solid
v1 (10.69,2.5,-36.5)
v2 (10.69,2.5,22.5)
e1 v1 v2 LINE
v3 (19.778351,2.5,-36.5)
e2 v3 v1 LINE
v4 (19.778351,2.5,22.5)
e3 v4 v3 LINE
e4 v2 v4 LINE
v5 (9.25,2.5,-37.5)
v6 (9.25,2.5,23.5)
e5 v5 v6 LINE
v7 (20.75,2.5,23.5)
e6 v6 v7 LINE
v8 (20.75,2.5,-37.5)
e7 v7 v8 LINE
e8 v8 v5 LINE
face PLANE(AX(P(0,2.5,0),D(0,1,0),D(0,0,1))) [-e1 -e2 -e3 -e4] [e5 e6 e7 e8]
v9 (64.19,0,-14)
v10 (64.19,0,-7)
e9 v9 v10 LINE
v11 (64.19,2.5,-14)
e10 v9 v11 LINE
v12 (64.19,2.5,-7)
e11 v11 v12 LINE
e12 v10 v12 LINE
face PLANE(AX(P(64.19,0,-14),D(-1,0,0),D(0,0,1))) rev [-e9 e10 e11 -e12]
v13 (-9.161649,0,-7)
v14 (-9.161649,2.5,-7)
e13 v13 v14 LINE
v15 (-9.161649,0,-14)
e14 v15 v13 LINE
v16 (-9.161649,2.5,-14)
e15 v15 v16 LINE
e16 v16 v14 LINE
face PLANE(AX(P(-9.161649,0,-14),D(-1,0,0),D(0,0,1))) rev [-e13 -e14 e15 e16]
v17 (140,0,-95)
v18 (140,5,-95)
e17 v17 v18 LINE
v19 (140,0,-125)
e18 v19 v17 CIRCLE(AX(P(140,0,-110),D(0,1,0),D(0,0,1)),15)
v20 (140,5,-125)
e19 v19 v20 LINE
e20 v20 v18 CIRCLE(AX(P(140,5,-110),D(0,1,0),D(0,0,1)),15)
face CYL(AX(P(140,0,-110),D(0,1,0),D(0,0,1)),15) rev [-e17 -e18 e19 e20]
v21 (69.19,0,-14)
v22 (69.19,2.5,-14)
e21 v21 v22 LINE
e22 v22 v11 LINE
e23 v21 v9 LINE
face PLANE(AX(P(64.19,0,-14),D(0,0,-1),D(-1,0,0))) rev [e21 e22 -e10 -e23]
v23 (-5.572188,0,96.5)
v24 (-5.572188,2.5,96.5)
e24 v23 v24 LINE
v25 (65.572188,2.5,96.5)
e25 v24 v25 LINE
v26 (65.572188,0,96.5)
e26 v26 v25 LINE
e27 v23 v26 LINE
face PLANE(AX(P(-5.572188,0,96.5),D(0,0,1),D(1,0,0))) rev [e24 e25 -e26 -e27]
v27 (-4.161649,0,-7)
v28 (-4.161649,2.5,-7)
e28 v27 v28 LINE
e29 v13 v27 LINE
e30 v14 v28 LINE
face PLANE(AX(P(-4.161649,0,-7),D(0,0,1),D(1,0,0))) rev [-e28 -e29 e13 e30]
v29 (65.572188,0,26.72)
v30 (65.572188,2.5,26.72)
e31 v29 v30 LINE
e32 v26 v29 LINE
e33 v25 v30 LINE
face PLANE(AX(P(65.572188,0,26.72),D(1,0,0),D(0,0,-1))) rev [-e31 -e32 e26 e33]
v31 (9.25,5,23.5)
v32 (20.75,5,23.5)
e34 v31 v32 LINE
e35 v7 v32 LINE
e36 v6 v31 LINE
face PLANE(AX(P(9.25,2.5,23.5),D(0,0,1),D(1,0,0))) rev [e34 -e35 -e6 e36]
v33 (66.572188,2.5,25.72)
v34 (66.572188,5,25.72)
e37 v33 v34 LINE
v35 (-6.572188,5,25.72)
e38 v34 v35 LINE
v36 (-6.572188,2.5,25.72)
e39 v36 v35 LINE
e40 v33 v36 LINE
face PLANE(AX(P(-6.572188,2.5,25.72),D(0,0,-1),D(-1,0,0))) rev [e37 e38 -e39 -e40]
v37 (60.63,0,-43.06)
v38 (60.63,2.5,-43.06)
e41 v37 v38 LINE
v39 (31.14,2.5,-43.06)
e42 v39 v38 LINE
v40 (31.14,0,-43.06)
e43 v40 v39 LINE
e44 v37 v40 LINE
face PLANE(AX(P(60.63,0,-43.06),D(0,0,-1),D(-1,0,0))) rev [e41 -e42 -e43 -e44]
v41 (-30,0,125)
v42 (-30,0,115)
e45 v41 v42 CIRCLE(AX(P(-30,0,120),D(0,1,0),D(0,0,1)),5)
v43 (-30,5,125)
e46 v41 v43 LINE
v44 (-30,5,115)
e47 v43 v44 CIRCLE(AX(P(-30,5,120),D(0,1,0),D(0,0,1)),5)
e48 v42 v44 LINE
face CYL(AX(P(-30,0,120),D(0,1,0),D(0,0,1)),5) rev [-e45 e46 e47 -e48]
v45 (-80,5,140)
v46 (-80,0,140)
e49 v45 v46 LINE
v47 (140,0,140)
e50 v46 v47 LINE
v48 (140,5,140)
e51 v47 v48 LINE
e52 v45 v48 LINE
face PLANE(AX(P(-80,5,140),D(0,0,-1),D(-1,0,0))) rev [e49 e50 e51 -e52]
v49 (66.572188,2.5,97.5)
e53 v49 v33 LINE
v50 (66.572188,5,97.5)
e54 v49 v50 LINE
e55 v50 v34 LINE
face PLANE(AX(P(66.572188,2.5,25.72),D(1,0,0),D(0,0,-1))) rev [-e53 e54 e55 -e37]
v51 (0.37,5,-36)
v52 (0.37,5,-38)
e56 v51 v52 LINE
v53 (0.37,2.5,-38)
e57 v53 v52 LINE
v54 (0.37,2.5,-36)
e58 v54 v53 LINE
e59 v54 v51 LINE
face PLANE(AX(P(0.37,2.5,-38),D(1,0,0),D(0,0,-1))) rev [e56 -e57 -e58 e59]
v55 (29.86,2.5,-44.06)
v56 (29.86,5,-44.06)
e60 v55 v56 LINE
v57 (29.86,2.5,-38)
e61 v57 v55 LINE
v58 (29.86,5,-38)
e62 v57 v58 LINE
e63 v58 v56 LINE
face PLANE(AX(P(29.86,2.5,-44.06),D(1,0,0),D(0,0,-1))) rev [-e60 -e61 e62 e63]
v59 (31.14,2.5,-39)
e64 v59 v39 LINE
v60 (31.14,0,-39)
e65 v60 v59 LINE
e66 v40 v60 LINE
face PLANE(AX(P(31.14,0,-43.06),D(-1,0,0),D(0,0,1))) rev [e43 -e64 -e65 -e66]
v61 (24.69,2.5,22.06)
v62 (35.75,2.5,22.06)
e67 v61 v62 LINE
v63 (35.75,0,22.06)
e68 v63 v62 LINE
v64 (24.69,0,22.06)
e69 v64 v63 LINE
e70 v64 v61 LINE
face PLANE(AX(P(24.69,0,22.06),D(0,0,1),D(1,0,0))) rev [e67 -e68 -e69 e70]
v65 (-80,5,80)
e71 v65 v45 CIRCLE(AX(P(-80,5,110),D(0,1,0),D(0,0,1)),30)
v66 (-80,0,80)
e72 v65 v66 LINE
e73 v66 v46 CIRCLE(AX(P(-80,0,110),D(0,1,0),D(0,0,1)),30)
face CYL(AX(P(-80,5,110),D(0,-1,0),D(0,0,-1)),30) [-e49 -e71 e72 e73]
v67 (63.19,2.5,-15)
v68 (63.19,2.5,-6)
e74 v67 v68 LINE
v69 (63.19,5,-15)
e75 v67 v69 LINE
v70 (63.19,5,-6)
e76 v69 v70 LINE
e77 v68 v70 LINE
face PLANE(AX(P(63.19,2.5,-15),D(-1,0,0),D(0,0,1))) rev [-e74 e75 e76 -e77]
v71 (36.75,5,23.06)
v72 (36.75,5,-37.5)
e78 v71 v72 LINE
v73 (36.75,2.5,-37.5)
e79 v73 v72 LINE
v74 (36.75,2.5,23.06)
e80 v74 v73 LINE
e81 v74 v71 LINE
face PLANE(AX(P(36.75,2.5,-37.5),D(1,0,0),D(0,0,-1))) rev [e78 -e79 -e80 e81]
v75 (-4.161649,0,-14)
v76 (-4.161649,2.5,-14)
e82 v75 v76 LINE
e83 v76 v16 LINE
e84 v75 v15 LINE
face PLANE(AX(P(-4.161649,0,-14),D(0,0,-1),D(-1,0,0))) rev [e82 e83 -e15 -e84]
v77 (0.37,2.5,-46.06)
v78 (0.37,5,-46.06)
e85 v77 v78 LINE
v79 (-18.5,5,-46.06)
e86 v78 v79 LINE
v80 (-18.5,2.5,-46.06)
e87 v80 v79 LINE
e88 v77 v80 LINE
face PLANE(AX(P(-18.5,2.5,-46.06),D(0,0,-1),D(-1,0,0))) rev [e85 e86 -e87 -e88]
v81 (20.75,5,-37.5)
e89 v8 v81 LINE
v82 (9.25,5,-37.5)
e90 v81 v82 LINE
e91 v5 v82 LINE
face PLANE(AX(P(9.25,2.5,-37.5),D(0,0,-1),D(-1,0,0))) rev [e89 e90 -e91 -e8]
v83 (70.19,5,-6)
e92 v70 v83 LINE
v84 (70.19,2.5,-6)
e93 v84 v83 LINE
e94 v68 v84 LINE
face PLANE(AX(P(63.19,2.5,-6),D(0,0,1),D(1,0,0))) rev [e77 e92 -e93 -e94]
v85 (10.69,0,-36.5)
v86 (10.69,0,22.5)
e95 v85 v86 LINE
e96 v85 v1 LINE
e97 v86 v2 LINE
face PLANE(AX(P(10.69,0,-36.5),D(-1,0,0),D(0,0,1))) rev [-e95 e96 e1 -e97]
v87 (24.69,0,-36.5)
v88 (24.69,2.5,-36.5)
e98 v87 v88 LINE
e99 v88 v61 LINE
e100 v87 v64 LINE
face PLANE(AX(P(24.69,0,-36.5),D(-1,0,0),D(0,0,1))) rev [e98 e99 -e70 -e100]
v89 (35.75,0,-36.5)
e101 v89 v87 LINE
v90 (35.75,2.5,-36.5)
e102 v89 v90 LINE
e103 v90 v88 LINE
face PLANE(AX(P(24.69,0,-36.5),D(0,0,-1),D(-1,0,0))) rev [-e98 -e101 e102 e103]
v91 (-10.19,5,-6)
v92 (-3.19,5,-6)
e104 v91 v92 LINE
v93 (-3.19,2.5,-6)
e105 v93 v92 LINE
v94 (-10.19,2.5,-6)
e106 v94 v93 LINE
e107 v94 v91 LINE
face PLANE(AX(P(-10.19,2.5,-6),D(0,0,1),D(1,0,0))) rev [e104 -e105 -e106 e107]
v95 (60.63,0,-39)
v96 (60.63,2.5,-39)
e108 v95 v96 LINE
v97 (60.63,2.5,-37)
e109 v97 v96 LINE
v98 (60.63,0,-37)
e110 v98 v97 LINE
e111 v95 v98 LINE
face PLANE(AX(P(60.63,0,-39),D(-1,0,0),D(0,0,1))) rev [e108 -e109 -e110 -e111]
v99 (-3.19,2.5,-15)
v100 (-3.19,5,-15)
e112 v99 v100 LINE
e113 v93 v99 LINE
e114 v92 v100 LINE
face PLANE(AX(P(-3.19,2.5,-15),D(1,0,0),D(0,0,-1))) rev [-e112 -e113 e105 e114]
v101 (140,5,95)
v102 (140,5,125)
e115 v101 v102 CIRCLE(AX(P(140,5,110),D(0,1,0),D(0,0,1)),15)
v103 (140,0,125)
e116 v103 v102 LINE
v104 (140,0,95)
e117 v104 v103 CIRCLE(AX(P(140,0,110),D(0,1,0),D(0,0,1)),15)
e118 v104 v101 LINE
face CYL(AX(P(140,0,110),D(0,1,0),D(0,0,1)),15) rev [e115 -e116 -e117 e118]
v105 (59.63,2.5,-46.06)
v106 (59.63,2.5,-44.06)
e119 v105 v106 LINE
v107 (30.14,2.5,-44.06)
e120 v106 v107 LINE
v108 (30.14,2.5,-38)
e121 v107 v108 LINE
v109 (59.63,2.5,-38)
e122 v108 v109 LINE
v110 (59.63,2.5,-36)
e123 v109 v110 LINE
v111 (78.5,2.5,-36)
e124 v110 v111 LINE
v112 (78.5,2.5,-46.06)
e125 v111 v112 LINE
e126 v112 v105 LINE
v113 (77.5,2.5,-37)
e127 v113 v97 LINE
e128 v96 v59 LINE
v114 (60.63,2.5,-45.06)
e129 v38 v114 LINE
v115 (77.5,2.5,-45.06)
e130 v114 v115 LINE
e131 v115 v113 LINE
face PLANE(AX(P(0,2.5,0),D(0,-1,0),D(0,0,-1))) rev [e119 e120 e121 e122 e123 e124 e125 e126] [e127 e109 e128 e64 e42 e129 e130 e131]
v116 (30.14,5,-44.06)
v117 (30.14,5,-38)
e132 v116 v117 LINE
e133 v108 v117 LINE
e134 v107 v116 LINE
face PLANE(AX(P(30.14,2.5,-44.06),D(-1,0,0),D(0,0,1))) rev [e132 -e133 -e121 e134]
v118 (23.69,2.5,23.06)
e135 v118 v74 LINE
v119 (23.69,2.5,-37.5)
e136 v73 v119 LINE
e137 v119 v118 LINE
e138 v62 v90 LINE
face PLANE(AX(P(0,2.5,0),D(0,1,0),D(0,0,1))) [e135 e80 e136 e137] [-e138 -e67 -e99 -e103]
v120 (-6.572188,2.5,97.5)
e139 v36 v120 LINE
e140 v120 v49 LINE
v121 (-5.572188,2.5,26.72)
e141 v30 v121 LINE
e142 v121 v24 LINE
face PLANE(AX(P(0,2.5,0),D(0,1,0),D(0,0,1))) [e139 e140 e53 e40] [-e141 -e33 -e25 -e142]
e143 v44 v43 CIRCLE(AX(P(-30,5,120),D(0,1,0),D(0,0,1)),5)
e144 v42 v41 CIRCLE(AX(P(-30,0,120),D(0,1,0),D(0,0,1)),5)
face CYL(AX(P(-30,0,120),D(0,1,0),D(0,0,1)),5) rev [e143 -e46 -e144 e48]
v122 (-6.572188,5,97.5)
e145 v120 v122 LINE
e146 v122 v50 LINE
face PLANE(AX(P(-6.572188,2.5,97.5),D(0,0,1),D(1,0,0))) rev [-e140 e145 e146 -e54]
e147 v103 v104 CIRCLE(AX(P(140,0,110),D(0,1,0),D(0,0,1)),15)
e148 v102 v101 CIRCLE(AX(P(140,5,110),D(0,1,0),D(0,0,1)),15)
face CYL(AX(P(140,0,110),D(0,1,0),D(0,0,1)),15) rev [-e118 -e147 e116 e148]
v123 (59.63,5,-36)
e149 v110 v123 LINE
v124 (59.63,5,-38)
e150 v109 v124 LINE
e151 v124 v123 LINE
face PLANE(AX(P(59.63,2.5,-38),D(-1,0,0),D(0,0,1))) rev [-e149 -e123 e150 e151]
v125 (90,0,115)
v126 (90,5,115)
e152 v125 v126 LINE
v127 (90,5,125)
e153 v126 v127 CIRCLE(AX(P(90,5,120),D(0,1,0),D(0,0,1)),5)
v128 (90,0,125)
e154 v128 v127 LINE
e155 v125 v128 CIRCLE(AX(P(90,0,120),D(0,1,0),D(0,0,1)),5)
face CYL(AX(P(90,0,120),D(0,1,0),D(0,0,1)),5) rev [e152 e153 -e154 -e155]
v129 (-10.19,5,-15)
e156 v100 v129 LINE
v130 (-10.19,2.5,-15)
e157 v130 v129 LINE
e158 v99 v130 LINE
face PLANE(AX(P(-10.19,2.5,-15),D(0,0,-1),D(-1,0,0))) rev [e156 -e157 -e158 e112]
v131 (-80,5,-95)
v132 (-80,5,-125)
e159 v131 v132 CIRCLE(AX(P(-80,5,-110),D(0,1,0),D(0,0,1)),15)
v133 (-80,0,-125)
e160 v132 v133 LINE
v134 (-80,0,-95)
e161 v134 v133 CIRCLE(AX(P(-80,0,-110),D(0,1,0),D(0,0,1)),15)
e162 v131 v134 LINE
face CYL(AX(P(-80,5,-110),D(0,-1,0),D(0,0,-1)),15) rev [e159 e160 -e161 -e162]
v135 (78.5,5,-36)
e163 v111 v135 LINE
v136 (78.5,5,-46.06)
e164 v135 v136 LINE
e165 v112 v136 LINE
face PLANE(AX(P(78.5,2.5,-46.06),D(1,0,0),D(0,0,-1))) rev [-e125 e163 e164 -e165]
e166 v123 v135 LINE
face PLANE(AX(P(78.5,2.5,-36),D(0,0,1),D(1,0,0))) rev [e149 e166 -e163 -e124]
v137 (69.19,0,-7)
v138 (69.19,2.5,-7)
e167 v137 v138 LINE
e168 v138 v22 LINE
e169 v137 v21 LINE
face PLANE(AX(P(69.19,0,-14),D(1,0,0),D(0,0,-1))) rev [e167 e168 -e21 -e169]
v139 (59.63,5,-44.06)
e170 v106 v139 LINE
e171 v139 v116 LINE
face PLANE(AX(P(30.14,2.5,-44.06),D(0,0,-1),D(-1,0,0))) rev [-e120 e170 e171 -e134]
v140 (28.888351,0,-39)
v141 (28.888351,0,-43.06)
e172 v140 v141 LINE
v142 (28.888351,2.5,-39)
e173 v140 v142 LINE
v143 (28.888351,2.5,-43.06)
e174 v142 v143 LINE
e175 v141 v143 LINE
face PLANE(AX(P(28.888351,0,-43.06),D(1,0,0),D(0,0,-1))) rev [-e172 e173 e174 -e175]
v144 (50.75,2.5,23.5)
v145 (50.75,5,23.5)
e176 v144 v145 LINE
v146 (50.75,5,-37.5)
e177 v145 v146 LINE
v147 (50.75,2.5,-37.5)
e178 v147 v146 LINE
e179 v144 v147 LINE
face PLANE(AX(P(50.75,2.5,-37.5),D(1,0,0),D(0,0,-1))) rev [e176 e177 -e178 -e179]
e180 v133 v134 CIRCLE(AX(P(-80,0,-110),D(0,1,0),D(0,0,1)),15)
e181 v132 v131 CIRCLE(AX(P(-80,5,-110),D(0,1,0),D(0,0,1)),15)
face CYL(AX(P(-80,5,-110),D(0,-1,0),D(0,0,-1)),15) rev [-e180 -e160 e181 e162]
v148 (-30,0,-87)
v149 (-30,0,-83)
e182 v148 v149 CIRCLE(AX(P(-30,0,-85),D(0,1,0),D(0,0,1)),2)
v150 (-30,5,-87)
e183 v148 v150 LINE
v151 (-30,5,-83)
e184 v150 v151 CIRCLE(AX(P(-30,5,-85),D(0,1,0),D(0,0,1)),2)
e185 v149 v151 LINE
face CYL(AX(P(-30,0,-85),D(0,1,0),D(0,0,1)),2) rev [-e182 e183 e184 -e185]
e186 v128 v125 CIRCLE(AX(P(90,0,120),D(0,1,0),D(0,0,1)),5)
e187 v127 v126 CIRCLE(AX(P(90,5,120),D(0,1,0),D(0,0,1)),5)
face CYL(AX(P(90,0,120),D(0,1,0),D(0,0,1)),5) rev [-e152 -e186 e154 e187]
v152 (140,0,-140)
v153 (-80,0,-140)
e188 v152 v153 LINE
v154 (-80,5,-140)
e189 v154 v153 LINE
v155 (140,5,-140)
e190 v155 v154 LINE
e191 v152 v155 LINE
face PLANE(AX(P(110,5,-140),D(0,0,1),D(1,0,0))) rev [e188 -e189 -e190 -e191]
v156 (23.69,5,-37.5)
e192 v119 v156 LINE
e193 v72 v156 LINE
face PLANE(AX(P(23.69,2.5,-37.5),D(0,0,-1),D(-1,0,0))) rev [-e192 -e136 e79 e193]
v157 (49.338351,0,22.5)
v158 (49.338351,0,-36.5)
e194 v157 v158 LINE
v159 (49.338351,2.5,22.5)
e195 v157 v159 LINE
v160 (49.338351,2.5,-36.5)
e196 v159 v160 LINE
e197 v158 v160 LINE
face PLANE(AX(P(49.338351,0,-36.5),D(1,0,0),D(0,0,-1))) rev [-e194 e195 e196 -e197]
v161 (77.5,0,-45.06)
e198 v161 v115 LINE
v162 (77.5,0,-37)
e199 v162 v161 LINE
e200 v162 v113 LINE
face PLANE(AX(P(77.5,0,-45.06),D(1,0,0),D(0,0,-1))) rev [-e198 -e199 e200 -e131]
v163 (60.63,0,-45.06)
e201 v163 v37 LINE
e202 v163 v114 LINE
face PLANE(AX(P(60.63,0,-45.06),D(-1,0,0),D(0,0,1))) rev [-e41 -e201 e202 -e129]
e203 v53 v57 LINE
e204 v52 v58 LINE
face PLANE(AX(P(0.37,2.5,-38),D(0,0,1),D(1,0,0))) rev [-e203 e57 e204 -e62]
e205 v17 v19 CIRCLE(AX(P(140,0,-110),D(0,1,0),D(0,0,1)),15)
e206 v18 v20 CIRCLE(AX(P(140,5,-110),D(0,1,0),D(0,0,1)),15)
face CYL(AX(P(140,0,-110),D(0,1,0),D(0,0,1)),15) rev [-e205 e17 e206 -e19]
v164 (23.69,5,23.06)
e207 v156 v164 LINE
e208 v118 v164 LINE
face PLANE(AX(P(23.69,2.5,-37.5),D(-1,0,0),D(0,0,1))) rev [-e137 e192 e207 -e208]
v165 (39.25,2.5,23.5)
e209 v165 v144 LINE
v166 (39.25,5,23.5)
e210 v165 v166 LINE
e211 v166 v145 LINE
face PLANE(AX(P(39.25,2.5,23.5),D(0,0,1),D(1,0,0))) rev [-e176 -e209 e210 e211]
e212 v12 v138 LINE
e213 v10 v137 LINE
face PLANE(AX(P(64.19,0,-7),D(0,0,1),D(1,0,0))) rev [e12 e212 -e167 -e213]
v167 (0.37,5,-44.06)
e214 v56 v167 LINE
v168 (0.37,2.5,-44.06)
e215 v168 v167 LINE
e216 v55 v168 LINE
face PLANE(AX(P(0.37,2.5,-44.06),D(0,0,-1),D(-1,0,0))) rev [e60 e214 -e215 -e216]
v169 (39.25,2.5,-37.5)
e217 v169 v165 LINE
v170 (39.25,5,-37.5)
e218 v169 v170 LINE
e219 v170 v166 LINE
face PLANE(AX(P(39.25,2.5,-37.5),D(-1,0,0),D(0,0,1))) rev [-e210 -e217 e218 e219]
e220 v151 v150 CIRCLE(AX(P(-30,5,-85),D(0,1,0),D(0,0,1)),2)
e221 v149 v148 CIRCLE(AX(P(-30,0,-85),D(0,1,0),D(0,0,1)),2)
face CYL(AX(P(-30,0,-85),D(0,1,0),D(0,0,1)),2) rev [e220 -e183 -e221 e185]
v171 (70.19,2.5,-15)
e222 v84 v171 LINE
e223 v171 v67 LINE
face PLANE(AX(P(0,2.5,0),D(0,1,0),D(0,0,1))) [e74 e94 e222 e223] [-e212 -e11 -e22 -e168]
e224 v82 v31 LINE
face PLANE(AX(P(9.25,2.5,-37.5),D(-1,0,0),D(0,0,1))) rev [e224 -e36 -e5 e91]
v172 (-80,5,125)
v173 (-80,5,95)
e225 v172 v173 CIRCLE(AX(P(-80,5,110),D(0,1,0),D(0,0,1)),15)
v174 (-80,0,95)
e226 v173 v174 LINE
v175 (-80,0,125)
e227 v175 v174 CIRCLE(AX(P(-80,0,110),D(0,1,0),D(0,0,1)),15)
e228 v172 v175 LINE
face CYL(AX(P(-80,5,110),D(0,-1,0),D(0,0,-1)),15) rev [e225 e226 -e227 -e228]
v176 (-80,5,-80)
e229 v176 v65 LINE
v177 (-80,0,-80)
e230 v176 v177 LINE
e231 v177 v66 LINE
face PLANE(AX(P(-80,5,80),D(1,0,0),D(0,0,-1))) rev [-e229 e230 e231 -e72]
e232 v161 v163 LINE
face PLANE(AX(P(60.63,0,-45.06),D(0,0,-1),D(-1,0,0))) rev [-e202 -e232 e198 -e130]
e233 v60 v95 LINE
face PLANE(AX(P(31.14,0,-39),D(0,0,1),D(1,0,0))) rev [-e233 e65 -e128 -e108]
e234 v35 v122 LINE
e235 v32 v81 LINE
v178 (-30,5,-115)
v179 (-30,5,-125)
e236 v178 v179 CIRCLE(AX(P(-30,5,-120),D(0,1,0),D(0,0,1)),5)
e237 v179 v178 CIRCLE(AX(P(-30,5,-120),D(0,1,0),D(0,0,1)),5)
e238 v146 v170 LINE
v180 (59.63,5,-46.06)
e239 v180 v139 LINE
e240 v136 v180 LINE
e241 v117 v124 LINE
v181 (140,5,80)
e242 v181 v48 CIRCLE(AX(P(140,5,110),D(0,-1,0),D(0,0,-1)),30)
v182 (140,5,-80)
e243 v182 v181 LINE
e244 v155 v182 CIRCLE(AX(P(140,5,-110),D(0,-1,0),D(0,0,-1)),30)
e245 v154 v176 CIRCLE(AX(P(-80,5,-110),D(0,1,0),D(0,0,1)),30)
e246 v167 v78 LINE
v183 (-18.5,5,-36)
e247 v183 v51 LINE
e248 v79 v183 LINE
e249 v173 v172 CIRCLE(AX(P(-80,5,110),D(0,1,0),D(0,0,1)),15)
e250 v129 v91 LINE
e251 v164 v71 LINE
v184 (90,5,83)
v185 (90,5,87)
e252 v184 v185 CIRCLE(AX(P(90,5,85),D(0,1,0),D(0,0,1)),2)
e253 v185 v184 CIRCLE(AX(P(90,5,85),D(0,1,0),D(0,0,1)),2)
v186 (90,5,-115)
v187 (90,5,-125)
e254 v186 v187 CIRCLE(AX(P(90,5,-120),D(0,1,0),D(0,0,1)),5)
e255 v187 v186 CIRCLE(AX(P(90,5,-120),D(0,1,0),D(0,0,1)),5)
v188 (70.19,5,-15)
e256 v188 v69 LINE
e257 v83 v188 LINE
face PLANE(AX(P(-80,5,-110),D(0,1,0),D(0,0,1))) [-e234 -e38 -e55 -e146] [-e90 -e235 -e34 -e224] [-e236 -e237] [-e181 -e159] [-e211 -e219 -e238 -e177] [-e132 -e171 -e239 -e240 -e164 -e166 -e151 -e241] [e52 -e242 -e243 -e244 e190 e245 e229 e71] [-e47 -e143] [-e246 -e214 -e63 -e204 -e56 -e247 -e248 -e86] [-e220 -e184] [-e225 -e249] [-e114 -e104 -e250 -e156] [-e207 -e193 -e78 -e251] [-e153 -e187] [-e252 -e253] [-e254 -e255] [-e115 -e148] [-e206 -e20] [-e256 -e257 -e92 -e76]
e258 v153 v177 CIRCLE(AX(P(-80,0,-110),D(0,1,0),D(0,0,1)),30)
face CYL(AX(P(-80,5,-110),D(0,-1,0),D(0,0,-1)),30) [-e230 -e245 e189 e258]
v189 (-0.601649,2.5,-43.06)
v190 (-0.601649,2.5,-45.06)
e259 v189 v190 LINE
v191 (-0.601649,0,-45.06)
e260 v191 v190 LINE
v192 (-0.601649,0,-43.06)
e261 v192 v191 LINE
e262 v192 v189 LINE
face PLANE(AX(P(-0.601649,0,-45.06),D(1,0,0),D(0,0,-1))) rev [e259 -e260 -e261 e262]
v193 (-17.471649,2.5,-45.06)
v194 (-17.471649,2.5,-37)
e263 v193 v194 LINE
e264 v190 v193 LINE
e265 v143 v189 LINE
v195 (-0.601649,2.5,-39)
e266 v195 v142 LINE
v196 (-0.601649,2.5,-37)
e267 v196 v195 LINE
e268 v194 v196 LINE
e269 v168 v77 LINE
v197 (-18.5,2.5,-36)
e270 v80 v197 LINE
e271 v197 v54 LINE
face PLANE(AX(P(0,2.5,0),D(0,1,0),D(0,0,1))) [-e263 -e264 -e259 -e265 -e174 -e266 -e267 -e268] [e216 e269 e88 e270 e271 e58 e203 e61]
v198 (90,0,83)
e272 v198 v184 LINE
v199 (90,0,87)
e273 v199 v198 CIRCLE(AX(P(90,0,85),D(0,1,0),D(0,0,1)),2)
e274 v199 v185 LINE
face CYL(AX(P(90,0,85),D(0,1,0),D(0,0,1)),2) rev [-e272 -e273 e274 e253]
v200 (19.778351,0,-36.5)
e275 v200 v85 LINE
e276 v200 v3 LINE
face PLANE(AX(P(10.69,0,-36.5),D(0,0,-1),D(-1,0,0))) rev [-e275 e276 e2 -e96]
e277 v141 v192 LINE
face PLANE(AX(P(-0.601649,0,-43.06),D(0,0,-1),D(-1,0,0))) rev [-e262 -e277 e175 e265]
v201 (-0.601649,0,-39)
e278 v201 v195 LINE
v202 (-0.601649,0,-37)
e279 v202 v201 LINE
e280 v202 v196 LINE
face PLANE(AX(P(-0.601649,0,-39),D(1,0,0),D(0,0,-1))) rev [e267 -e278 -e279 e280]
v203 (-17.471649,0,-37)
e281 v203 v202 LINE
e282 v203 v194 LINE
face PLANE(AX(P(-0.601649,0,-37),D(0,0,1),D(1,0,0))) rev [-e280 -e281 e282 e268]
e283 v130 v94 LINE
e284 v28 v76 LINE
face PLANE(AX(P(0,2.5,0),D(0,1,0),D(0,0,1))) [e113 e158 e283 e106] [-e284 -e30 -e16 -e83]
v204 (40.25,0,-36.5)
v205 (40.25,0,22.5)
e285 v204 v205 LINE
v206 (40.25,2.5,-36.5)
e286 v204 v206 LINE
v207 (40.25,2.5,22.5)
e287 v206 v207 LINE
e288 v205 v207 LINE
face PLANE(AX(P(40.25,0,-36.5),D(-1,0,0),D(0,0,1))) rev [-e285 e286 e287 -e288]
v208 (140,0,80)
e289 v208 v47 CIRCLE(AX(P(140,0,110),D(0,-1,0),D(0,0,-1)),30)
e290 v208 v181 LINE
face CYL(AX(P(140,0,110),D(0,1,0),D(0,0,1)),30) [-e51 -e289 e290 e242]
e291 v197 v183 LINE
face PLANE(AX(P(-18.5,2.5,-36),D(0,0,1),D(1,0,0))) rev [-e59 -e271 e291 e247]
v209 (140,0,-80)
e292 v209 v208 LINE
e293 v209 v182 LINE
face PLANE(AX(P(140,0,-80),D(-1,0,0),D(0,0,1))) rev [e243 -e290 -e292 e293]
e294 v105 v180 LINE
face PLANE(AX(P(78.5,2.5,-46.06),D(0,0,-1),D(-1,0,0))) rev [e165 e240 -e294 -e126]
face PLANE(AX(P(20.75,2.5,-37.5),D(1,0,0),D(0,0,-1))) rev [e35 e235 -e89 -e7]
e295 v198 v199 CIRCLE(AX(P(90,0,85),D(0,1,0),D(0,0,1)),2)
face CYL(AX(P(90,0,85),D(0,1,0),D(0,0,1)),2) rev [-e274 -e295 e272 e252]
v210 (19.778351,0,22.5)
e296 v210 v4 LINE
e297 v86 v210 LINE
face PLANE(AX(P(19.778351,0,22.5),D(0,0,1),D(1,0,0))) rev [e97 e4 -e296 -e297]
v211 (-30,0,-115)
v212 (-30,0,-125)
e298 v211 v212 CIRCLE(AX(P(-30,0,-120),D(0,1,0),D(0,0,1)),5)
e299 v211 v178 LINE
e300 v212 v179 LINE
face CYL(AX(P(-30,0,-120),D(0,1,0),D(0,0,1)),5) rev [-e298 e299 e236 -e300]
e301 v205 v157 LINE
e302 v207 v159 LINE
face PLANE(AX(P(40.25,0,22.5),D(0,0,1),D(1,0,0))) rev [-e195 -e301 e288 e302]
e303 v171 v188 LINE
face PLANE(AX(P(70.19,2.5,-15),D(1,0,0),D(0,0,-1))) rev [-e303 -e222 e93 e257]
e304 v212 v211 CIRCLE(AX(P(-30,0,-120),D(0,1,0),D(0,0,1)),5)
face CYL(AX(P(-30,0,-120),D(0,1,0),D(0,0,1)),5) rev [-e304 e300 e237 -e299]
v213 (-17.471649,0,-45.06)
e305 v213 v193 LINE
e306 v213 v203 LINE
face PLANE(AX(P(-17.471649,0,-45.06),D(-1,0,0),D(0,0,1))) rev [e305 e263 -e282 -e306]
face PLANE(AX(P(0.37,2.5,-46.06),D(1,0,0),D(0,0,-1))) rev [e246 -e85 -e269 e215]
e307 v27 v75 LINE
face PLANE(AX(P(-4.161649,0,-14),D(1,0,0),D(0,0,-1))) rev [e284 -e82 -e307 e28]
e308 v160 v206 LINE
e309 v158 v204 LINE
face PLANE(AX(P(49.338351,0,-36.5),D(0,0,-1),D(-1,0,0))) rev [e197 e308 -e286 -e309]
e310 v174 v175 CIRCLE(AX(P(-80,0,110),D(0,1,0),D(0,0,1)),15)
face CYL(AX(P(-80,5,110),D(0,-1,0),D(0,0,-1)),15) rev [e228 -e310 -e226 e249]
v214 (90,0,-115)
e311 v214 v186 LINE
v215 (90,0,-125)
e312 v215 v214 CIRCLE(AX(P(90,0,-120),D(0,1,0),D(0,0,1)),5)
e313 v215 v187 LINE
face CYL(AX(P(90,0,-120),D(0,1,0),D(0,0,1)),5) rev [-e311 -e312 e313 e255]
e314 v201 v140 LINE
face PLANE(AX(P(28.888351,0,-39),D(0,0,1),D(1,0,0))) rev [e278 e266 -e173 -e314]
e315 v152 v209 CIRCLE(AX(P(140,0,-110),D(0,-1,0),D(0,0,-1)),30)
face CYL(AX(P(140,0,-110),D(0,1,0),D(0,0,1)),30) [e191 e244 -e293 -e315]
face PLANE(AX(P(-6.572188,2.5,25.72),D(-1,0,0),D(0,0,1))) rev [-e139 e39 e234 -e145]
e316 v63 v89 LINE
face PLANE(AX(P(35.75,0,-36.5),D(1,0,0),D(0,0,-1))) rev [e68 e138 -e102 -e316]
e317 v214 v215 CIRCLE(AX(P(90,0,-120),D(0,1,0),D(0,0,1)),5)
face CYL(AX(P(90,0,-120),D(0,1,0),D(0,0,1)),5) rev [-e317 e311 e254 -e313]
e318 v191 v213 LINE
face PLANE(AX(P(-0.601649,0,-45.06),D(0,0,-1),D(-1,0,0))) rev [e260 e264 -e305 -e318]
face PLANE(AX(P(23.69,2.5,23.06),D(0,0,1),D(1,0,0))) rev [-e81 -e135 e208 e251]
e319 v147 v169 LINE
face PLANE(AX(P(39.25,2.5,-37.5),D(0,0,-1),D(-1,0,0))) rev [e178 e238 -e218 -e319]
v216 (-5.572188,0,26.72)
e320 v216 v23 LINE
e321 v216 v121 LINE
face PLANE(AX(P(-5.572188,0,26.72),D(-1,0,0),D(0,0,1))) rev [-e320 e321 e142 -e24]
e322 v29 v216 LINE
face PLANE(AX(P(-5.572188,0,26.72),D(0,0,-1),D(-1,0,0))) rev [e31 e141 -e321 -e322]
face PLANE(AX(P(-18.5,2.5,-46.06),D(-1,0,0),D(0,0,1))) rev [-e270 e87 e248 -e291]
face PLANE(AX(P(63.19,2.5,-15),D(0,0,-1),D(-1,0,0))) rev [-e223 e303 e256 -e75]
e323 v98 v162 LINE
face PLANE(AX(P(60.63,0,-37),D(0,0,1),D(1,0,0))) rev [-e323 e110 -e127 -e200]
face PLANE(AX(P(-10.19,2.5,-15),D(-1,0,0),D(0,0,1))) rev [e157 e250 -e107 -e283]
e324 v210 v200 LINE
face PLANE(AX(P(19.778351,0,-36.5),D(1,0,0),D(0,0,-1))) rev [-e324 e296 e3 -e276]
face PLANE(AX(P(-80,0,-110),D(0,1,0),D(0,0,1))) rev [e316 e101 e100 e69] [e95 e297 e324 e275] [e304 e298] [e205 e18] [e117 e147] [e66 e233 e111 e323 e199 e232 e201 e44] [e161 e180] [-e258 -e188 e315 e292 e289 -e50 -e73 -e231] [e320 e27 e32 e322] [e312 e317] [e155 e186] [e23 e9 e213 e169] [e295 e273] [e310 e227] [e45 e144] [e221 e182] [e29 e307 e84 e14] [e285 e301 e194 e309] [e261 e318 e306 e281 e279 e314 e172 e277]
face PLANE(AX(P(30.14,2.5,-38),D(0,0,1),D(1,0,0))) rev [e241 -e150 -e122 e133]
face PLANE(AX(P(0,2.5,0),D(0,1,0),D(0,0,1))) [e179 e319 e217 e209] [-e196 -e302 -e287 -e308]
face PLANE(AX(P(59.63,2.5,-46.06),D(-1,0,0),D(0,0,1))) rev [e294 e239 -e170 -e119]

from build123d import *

# Parameters (mm, degrees)
SKETCH2_R           = 15
BOSS_EXTRUDE1_DEPTH = 5
SKETCH3_W           = 73.144376366
SKETCH3_H           = 71.78
SKETCH3_W_2         = 7
SKETCH3_H_2         = 9
SKETCH3_W_3         = 11.5
SKETCH3_H_3         = 61
SKETCH3_W_4         = 13.06
SKETCH3_H_4         = 60.56
CUT_EXTRUDE1_DEPTH  = 2.5
SKETCH4_W           = 11.06
SKETCH4_H           = 58.56
SKETCH4_W_2         = 9.088350763
SKETCH4_H_2         = 59
SKETCH4_W_3         = 5
SKETCH4_H_3         = 7
SKETCH4_W_4         = 71.144376366
SKETCH4_H_4         = 69.78
CUT_EXTRUDE3_DEPTH  = 5
SKETCH5_R           = 5
CUT_EXTRUDE4_DEPTH  = 179.115131306
BOSS_EXTRUDE2_DEPTH = 5
SKETCH_2_R          = 15
CUT_EXTRUDE2_DEPTH  = 5
SKETCH_3_R          = 2
CUT_EXTRUDE_3_DEPTH = 221.283907719


with BuildPart() as part:
    # Sketch2 → Boss-Extrude1 (new body)
    with BuildSketch(Plane(origin=(0, 0, 0), x_dir=(1, 0, 0), z_dir=(0, 1, 0))):
        with BuildLine():
            Line((-80, -140), (110, -140))
            Line((110, -140), (110, 140))
            Line((110, 140), (-80, 140))
            ThreePointArc((-80, 140), (-110, 110), (-80, 80))
            Line((-80, 80), (-80, -80))
            ThreePointArc((-80, -80), (-110, -110), (-80, -140))
        make_face()
        with Locations(Location((-80, 110, 0), (0, 0, 270))):
            Circle(SKETCH2_R, mode=Mode.SUBTRACT)
        with Locations(Location((-80, -110, 0), (0, 0, 270))):
            Circle(SKETCH2_R, mode=Mode.SUBTRACT)
    extrude(amount=BOSS_EXTRUDE1_DEPTH)

    # Sketch3 → Cut-Extrude1 (cut)
    with BuildSketch(Plane(origin=(0, 5, 0), x_dir=(1, 0, 0), z_dir=(0, 1, 0))):
        Polygon((0.37, 46.06), (0.37, 44.06), (29.86, 44.06), (29.86, 38), (0.37, 38), (0.37, 36), (-18.5, 36), (-18.5, 46.06), align=None)
        with Locations((30, -61.61)):
            Rectangle(SKETCH3_W, SKETCH3_H)
        with Locations((-6.69, 10.5)):
            Rectangle(SKETCH3_W_2, SKETCH3_H_2)
        with Locations((66.69, 10.5)):
            Rectangle(SKETCH3_W_2, SKETCH3_H_2)
        with Locations((45, 7)):
            Rectangle(SKETCH3_W_3, SKETCH3_H_3)
        with Locations((30.22, 7.22)):
            Rectangle(SKETCH3_W_4, SKETCH3_H_4)
        with Locations((15, 7)):
            Rectangle(SKETCH3_W_3, SKETCH3_H_3)
        Polygon((78.5, 46.06), (59.63, 46.06), (59.63, 44.06), (30.14, 44.06), (30.14, 38), (59.63, 38), (59.63, 36), (78.5, 36), align=None)
    extrude(amount=-CUT_EXTRUDE1_DEPTH, mode=Mode.SUBTRACT)

    # Sketch4 → Cut-Extrude3 (cut)
    with BuildSketch(Plane(origin=(0, 5, 0), x_dir=(1, 0, 0), z_dir=(0, 1, 0))):
        with Locations((30.22, 7.22)):
            Rectangle(SKETCH4_W, SKETCH4_H)
        Polygon((-0.601649237, 45.06), (-0.601649237, 43.06), (28.888350763, 43.06), (28.888350763, 39), (-0.601649237, 39), (-0.601649237, 37), (-17.471649237, 37), (-17.471649237, 45.06), align=None)
        Polygon((31.14, 43.06), (31.14, 39), (60.63, 39), (60.63, 37), (77.5, 37), (77.5, 45.06), (60.63, 45.06), (60.63, 43.06), align=None)
        with Locations((44.794175381, 7)):
            Rectangle(SKETCH4_W_2, SKETCH4_H_2)
        with Locations((66.69, 10.5)):
            Rectangle(SKETCH4_W_3, SKETCH4_H_3)
        with Locations((30, -61.61)):
            Rectangle(SKETCH4_W_4, SKETCH4_H_4)
        with Locations((15.234175382, 7)):
            Rectangle(SKETCH4_W_2, SKETCH4_H_2)
        with Locations((-6.661649237, 10.5)):
            Rectangle(SKETCH4_W_3, SKETCH4_H_3)
    extrude(amount=-CUT_EXTRUDE3_DEPTH, mode=Mode.SUBTRACT)

    # Sketch5 → Cut-Extrude4 (cut, through all)
    with BuildSketch(Plane(origin=(0, 5, 0), x_dir=(1, 0, 0), z_dir=(0, 1, 0))):
        with Locations(Location((-30, 120, 0), (0, 0, 270))):
            Circle(SKETCH5_R)
        with Locations(Location((90, 120, 0), (0, 0, 270))):
            Circle(SKETCH5_R)
        with Locations(Location((90, -120, 0), (0, 0, 270))):
            Circle(SKETCH5_R)
        with Locations(Location((-30, -120, 0), (0, 0, 270))):
            Circle(SKETCH5_R)
    extrude(amount=-CUT_EXTRUDE4_DEPTH, mode=Mode.SUBTRACT)

    # Sketch1 → Boss-Extrude2 (add)
    with BuildSketch(Plane(origin=(0, 5, 0), x_dir=(1, 0, 0), z_dir=(0, 1, 0))):
        with BuildLine():
            Line((108.024540476, 140), (140, 140))
            ThreePointArc((140, 140), (170, 110), (140, 80))
            Line((140, 80), (140, -80))
            ThreePointArc((140, -80), (170, -110), (140, -140))
            Line((140, -140), (108.024540476, -140))
            Line((108.024540476, -140), (108.024540476, 140))
        make_face()
    extrude(amount=-BOSS_EXTRUDE2_DEPTH)

    # 草图2 → Cut-Extrude2 (cut)
    with BuildSketch(Plane(origin=(0, 5, 0), x_dir=(1, 0, 0), z_dir=(0, 1, 0))):
        with Locations(Location((140, 110, 0), (0, 0, 270))):
            Circle(SKETCH_2_R)
        with Locations(Location((140, -110, 0), (0, 0, 270))):
            Circle(SKETCH_2_R)
    extrude(amount=-CUT_EXTRUDE2_DEPTH, mode=Mode.SUBTRACT)

    # 草图3 → 切除-拉伸3 (cut, through all)
    with BuildSketch(Plane(origin=(0, 5, 0), x_dir=(1, 0, 0), z_dir=(0, 1, 0))):
        with Locations(Location((-30, 85, 0), (0, 0, 270))):
            Circle(SKETCH_3_R)
        with Locations(Location((90, -85, 0), (0, 0, 270))):
            Circle(SKETCH_3_R)
    extrude(amount=-CUT_EXTRUDE_3_DEPTH, mode=Mode.SUBTRACT)


solid = part.part
